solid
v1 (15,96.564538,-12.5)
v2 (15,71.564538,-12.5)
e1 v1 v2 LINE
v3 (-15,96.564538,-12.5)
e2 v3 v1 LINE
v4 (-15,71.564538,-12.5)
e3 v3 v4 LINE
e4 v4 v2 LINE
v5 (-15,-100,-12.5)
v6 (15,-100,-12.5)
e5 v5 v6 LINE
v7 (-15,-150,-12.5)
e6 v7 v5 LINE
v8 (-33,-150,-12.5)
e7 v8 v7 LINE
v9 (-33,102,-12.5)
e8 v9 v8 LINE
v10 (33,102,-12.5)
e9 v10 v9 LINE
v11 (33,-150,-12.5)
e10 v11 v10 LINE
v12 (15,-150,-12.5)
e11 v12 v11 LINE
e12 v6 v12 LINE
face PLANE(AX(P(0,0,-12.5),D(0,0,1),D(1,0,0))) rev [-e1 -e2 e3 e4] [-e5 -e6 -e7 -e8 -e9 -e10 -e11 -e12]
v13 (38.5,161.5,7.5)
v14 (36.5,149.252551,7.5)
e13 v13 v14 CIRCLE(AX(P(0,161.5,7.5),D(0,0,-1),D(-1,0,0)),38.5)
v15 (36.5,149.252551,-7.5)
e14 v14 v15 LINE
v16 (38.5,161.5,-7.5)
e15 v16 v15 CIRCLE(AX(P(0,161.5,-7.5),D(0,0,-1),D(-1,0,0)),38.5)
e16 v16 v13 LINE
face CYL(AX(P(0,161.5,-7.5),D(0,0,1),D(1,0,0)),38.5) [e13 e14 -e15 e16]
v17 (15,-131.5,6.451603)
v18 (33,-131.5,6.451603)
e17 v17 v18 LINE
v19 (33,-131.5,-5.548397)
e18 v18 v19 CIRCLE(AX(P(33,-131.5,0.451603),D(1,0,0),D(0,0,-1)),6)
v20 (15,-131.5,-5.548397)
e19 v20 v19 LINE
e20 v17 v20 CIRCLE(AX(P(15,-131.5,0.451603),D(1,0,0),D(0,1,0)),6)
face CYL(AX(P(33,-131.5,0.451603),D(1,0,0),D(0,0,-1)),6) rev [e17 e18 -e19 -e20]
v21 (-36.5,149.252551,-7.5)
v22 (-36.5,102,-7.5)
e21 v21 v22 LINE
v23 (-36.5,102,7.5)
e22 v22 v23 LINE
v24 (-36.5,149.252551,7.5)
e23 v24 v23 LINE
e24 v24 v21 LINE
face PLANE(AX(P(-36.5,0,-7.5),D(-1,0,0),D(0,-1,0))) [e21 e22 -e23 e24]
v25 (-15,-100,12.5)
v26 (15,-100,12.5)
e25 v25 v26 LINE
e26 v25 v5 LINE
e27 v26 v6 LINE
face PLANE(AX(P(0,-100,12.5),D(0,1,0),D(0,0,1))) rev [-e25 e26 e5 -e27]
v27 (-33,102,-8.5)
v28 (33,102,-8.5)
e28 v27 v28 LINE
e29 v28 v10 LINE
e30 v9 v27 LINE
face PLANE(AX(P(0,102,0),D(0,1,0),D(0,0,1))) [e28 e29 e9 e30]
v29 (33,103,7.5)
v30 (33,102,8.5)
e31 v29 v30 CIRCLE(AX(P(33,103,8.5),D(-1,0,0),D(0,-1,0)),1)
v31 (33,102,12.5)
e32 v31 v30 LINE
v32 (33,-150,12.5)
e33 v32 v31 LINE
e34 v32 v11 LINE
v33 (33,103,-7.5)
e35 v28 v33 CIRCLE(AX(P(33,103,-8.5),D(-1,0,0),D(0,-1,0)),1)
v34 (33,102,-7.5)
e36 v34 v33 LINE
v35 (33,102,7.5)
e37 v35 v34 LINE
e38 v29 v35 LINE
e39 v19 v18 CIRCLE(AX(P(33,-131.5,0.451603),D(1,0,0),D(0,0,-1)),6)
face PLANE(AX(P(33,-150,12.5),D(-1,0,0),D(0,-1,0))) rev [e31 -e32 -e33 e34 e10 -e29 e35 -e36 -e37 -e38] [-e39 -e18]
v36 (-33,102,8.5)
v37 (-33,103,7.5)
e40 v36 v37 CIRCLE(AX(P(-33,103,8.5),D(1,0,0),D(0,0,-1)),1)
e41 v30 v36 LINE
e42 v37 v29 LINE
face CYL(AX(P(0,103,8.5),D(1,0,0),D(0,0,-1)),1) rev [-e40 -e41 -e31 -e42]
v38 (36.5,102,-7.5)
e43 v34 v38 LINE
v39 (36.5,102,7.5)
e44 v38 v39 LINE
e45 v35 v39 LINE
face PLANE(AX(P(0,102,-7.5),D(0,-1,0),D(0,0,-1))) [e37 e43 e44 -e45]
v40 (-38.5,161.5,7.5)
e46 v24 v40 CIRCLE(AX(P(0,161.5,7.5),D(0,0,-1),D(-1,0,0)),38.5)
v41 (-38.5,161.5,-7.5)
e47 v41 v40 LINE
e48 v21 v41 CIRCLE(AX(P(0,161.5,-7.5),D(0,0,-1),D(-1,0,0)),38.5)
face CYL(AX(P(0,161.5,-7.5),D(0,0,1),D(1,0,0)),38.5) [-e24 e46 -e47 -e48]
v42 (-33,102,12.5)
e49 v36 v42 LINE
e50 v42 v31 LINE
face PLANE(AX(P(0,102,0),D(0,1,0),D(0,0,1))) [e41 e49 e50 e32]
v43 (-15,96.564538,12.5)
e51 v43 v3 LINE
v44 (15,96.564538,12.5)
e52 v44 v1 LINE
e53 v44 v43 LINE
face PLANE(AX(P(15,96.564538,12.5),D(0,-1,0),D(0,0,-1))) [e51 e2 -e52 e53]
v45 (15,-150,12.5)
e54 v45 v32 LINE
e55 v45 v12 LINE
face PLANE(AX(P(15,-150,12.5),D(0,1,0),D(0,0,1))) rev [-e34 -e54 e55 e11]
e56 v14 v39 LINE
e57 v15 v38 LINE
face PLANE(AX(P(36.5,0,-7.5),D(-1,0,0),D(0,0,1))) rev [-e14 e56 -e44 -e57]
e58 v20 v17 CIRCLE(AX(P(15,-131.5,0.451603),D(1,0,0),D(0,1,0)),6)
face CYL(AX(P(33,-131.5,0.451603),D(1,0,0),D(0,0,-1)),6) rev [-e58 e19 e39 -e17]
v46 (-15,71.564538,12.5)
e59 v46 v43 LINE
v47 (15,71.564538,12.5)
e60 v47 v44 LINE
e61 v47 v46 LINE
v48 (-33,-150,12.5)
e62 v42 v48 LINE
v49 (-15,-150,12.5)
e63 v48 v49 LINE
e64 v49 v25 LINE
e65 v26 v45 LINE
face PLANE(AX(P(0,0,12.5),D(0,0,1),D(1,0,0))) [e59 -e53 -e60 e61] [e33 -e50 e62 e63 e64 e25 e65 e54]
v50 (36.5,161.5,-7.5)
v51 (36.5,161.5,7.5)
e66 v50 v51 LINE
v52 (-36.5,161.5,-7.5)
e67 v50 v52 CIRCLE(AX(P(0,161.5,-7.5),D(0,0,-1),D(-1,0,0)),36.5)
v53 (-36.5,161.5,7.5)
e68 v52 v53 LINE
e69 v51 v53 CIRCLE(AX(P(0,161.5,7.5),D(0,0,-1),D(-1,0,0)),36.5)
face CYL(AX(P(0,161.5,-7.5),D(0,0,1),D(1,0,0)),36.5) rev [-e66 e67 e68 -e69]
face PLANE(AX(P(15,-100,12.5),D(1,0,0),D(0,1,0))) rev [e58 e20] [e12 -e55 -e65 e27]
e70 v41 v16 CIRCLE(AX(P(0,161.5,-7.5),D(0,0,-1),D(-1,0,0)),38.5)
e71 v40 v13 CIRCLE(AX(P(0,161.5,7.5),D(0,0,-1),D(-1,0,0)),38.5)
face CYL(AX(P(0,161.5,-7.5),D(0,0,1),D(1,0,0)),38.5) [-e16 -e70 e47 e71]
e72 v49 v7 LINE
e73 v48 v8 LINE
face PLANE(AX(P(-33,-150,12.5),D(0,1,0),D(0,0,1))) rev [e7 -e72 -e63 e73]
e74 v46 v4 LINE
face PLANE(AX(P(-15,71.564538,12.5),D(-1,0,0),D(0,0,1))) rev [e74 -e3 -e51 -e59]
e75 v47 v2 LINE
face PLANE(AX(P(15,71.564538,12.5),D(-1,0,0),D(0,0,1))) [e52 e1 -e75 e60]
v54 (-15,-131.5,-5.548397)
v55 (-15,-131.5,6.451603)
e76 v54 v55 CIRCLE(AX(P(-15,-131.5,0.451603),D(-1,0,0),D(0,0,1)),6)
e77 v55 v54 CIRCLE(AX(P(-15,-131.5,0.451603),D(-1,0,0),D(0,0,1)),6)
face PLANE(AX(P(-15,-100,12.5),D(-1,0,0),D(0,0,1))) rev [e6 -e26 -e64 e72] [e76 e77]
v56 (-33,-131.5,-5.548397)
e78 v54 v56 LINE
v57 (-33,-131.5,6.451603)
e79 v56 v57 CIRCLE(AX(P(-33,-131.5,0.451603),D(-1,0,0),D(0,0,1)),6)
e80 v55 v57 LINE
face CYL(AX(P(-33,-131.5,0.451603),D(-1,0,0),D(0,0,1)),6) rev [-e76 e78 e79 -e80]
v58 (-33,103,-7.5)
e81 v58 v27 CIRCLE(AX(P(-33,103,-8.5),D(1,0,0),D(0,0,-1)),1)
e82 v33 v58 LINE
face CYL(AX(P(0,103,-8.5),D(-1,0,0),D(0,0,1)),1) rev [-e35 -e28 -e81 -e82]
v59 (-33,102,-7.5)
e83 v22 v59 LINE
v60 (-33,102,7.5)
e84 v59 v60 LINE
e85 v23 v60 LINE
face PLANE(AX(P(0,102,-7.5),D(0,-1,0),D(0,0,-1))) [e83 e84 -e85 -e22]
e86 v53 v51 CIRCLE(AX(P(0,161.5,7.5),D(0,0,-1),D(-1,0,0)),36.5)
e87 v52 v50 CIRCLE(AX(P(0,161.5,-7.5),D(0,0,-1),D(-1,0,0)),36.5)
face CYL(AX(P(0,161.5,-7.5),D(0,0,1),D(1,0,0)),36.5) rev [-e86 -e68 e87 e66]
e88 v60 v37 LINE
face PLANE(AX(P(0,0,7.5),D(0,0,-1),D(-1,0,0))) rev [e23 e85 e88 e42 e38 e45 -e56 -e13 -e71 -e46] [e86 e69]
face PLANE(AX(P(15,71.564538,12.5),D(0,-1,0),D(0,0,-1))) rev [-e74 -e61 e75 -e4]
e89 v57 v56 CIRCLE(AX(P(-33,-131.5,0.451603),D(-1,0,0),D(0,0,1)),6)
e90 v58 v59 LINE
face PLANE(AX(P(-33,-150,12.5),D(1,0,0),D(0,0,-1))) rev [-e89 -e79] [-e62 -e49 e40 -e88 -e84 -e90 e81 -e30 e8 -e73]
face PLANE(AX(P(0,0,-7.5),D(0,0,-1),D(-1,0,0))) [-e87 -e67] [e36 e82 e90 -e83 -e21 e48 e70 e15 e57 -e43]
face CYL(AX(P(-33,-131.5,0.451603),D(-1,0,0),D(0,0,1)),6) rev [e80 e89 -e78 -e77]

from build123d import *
from build123d.topology import SkipClean

# Parameters (mm, degrees)
EXTRUDE_1_DEPTH          = 12.5
HOLE_WIZARD_M14_1_D      = 12
HOLE_WIZARD_M14_1_DEPTH  = 18
SKETCH_7_W               = 66
SKETCH_7_H               = 25
EXTRUDE_2_DEPTH          = 12
CUT_EXTRUDE_1_DEPTH      = 156.608483059
CUT_EXTRUDE_1_DEPTH_BACK = 156.608483059
SKETCH_14_W              = 30
SKETCH_14_H              = 25
EXTRUDE_START            = -12.5
EXTRUDE_3_DEPTH          = 7.5
SKETCH_8_4_R             = 38.5
SKETCH_8_4_R_2           = 36.5
EXTRUDE_1_2_DEPTH        = 7.5
FILLET_1_R               = 1


with BuildPart() as part:
    # 草图1 → Extrude 1 (new, symmetric)
    with BuildSketch(Plane.XY):
        Polygon((-33, -150), (-15, -150), (-15, -100), (0, -100), (15, -100), (15, -150), (33, -150), (33, 90), (15, 90), (-15, 90), (-33, 90), align=None)
    extrude(amount=EXTRUDE_1_DEPTH, both=True)

    # M14 螺纹孔1
    with Locations(Plane(origin=(33, -131.5, 0.451602972), x_dir=(0, 0, 1), z_dir=(1, 0, 0))):
        with Locations((0, 0)):
            hole_wizard_m14_1 = Hole(HOLE_WIZARD_M14_1_D / 2, depth=HOLE_WIZARD_M14_1_DEPTH)

    # 镜向1: M14 螺纹孔1 across plane
    add(hole_wizard_m14_1.mirror(Plane(origin=(0, 0, 0), x_dir=(0, 0, 1), z_dir=(1, 0, 0))), mode=Mode.SUBTRACT)

    # 草图7 → 凸台-拉伸2 (add)
    with BuildSketch(Plane(origin=(0, 90, 0), x_dir=(1, 0, 0), z_dir=(0, 1, 0))):
        Rectangle(SKETCH_7_W, SKETCH_7_H)
    extrude(amount=EXTRUDE_2_DEPTH)

    # 草图14 → 切除-拉伸1 (cut, two sides: drawn at the far end of the back side and taken through both)
    with BuildSketch(Plane(origin=(0, 0, -12.5), x_dir=(-1, 0, 0), z_dir=(0, 0, -1)).offset(-CUT_EXTRUDE_1_DEPTH_BACK)):
        with Locations((0, 84.064537633)):
            Rectangle(SKETCH_14_W, SKETCH_14_H)
    extrude(amount=CUT_EXTRUDE_1_DEPTH + CUT_EXTRUDE_1_DEPTH_BACK, mode=Mode.SUBTRACT)

    # 草图8 → 凸台-拉伸3 (add, symmetric)
    with BuildSketch(Plane(origin=(0, 0, -12.5), x_dir=(-1, 0, 0), z_dir=(0, 0, -1)).offset(EXTRUDE_START)):
        with BuildLine():
            Line((-33, 102), (0, 102))
            Line((0, 102), (0, 125))
            ThreePointArc((0, 125), (-25.809397513, 135.690602487), (-36.5, 161.5))
            Line((-36.5, 161.5), (-36.5, 102))
            Line((-36.5, 102), (-33, 102))
        make_face()
        with BuildLine():
            Line((0, 102), (33, 102))
            Line((33, 102), (36.5, 102))
            Line((36.5, 102), (36.5, 161.5))
            ThreePointArc((36.5, 161.5), (25.809397513, 135.690602487), (0, 125))
            Line((0, 125), (0, 102))
        make_face()
    extrude(amount=EXTRUDE_3_DEPTH, both=True)

    # 草图8<4> → Extrude 1 2 (add, symmetric)
    with SkipClean():  # the faces are left unmerged after this step: merging them gives an invalid solid
        with BuildSketch(Plane(origin=(0, 0, -12.5), x_dir=(-1, 0, 0), z_dir=(0, 0, -1)).offset(EXTRUDE_START)):
            with Locations((0, 161.5)):
                Circle(SKETCH_8_4_R)
            with Locations((0, 161.5)):
                Circle(SKETCH_8_4_R_2, mode=Mode.SUBTRACT)
        extrude(amount=EXTRUDE_1_2_DEPTH, both=True)

    # 圆角1
    fillet_1_edges = [part.edges().sort_by_distance(p)[0] for p in [
        (0, 102, -7.5),
        (0, 102, 7.5),
    ]]
    fillet(fillet_1_edges, radius=FILLET_1_R)


solid = part.part
